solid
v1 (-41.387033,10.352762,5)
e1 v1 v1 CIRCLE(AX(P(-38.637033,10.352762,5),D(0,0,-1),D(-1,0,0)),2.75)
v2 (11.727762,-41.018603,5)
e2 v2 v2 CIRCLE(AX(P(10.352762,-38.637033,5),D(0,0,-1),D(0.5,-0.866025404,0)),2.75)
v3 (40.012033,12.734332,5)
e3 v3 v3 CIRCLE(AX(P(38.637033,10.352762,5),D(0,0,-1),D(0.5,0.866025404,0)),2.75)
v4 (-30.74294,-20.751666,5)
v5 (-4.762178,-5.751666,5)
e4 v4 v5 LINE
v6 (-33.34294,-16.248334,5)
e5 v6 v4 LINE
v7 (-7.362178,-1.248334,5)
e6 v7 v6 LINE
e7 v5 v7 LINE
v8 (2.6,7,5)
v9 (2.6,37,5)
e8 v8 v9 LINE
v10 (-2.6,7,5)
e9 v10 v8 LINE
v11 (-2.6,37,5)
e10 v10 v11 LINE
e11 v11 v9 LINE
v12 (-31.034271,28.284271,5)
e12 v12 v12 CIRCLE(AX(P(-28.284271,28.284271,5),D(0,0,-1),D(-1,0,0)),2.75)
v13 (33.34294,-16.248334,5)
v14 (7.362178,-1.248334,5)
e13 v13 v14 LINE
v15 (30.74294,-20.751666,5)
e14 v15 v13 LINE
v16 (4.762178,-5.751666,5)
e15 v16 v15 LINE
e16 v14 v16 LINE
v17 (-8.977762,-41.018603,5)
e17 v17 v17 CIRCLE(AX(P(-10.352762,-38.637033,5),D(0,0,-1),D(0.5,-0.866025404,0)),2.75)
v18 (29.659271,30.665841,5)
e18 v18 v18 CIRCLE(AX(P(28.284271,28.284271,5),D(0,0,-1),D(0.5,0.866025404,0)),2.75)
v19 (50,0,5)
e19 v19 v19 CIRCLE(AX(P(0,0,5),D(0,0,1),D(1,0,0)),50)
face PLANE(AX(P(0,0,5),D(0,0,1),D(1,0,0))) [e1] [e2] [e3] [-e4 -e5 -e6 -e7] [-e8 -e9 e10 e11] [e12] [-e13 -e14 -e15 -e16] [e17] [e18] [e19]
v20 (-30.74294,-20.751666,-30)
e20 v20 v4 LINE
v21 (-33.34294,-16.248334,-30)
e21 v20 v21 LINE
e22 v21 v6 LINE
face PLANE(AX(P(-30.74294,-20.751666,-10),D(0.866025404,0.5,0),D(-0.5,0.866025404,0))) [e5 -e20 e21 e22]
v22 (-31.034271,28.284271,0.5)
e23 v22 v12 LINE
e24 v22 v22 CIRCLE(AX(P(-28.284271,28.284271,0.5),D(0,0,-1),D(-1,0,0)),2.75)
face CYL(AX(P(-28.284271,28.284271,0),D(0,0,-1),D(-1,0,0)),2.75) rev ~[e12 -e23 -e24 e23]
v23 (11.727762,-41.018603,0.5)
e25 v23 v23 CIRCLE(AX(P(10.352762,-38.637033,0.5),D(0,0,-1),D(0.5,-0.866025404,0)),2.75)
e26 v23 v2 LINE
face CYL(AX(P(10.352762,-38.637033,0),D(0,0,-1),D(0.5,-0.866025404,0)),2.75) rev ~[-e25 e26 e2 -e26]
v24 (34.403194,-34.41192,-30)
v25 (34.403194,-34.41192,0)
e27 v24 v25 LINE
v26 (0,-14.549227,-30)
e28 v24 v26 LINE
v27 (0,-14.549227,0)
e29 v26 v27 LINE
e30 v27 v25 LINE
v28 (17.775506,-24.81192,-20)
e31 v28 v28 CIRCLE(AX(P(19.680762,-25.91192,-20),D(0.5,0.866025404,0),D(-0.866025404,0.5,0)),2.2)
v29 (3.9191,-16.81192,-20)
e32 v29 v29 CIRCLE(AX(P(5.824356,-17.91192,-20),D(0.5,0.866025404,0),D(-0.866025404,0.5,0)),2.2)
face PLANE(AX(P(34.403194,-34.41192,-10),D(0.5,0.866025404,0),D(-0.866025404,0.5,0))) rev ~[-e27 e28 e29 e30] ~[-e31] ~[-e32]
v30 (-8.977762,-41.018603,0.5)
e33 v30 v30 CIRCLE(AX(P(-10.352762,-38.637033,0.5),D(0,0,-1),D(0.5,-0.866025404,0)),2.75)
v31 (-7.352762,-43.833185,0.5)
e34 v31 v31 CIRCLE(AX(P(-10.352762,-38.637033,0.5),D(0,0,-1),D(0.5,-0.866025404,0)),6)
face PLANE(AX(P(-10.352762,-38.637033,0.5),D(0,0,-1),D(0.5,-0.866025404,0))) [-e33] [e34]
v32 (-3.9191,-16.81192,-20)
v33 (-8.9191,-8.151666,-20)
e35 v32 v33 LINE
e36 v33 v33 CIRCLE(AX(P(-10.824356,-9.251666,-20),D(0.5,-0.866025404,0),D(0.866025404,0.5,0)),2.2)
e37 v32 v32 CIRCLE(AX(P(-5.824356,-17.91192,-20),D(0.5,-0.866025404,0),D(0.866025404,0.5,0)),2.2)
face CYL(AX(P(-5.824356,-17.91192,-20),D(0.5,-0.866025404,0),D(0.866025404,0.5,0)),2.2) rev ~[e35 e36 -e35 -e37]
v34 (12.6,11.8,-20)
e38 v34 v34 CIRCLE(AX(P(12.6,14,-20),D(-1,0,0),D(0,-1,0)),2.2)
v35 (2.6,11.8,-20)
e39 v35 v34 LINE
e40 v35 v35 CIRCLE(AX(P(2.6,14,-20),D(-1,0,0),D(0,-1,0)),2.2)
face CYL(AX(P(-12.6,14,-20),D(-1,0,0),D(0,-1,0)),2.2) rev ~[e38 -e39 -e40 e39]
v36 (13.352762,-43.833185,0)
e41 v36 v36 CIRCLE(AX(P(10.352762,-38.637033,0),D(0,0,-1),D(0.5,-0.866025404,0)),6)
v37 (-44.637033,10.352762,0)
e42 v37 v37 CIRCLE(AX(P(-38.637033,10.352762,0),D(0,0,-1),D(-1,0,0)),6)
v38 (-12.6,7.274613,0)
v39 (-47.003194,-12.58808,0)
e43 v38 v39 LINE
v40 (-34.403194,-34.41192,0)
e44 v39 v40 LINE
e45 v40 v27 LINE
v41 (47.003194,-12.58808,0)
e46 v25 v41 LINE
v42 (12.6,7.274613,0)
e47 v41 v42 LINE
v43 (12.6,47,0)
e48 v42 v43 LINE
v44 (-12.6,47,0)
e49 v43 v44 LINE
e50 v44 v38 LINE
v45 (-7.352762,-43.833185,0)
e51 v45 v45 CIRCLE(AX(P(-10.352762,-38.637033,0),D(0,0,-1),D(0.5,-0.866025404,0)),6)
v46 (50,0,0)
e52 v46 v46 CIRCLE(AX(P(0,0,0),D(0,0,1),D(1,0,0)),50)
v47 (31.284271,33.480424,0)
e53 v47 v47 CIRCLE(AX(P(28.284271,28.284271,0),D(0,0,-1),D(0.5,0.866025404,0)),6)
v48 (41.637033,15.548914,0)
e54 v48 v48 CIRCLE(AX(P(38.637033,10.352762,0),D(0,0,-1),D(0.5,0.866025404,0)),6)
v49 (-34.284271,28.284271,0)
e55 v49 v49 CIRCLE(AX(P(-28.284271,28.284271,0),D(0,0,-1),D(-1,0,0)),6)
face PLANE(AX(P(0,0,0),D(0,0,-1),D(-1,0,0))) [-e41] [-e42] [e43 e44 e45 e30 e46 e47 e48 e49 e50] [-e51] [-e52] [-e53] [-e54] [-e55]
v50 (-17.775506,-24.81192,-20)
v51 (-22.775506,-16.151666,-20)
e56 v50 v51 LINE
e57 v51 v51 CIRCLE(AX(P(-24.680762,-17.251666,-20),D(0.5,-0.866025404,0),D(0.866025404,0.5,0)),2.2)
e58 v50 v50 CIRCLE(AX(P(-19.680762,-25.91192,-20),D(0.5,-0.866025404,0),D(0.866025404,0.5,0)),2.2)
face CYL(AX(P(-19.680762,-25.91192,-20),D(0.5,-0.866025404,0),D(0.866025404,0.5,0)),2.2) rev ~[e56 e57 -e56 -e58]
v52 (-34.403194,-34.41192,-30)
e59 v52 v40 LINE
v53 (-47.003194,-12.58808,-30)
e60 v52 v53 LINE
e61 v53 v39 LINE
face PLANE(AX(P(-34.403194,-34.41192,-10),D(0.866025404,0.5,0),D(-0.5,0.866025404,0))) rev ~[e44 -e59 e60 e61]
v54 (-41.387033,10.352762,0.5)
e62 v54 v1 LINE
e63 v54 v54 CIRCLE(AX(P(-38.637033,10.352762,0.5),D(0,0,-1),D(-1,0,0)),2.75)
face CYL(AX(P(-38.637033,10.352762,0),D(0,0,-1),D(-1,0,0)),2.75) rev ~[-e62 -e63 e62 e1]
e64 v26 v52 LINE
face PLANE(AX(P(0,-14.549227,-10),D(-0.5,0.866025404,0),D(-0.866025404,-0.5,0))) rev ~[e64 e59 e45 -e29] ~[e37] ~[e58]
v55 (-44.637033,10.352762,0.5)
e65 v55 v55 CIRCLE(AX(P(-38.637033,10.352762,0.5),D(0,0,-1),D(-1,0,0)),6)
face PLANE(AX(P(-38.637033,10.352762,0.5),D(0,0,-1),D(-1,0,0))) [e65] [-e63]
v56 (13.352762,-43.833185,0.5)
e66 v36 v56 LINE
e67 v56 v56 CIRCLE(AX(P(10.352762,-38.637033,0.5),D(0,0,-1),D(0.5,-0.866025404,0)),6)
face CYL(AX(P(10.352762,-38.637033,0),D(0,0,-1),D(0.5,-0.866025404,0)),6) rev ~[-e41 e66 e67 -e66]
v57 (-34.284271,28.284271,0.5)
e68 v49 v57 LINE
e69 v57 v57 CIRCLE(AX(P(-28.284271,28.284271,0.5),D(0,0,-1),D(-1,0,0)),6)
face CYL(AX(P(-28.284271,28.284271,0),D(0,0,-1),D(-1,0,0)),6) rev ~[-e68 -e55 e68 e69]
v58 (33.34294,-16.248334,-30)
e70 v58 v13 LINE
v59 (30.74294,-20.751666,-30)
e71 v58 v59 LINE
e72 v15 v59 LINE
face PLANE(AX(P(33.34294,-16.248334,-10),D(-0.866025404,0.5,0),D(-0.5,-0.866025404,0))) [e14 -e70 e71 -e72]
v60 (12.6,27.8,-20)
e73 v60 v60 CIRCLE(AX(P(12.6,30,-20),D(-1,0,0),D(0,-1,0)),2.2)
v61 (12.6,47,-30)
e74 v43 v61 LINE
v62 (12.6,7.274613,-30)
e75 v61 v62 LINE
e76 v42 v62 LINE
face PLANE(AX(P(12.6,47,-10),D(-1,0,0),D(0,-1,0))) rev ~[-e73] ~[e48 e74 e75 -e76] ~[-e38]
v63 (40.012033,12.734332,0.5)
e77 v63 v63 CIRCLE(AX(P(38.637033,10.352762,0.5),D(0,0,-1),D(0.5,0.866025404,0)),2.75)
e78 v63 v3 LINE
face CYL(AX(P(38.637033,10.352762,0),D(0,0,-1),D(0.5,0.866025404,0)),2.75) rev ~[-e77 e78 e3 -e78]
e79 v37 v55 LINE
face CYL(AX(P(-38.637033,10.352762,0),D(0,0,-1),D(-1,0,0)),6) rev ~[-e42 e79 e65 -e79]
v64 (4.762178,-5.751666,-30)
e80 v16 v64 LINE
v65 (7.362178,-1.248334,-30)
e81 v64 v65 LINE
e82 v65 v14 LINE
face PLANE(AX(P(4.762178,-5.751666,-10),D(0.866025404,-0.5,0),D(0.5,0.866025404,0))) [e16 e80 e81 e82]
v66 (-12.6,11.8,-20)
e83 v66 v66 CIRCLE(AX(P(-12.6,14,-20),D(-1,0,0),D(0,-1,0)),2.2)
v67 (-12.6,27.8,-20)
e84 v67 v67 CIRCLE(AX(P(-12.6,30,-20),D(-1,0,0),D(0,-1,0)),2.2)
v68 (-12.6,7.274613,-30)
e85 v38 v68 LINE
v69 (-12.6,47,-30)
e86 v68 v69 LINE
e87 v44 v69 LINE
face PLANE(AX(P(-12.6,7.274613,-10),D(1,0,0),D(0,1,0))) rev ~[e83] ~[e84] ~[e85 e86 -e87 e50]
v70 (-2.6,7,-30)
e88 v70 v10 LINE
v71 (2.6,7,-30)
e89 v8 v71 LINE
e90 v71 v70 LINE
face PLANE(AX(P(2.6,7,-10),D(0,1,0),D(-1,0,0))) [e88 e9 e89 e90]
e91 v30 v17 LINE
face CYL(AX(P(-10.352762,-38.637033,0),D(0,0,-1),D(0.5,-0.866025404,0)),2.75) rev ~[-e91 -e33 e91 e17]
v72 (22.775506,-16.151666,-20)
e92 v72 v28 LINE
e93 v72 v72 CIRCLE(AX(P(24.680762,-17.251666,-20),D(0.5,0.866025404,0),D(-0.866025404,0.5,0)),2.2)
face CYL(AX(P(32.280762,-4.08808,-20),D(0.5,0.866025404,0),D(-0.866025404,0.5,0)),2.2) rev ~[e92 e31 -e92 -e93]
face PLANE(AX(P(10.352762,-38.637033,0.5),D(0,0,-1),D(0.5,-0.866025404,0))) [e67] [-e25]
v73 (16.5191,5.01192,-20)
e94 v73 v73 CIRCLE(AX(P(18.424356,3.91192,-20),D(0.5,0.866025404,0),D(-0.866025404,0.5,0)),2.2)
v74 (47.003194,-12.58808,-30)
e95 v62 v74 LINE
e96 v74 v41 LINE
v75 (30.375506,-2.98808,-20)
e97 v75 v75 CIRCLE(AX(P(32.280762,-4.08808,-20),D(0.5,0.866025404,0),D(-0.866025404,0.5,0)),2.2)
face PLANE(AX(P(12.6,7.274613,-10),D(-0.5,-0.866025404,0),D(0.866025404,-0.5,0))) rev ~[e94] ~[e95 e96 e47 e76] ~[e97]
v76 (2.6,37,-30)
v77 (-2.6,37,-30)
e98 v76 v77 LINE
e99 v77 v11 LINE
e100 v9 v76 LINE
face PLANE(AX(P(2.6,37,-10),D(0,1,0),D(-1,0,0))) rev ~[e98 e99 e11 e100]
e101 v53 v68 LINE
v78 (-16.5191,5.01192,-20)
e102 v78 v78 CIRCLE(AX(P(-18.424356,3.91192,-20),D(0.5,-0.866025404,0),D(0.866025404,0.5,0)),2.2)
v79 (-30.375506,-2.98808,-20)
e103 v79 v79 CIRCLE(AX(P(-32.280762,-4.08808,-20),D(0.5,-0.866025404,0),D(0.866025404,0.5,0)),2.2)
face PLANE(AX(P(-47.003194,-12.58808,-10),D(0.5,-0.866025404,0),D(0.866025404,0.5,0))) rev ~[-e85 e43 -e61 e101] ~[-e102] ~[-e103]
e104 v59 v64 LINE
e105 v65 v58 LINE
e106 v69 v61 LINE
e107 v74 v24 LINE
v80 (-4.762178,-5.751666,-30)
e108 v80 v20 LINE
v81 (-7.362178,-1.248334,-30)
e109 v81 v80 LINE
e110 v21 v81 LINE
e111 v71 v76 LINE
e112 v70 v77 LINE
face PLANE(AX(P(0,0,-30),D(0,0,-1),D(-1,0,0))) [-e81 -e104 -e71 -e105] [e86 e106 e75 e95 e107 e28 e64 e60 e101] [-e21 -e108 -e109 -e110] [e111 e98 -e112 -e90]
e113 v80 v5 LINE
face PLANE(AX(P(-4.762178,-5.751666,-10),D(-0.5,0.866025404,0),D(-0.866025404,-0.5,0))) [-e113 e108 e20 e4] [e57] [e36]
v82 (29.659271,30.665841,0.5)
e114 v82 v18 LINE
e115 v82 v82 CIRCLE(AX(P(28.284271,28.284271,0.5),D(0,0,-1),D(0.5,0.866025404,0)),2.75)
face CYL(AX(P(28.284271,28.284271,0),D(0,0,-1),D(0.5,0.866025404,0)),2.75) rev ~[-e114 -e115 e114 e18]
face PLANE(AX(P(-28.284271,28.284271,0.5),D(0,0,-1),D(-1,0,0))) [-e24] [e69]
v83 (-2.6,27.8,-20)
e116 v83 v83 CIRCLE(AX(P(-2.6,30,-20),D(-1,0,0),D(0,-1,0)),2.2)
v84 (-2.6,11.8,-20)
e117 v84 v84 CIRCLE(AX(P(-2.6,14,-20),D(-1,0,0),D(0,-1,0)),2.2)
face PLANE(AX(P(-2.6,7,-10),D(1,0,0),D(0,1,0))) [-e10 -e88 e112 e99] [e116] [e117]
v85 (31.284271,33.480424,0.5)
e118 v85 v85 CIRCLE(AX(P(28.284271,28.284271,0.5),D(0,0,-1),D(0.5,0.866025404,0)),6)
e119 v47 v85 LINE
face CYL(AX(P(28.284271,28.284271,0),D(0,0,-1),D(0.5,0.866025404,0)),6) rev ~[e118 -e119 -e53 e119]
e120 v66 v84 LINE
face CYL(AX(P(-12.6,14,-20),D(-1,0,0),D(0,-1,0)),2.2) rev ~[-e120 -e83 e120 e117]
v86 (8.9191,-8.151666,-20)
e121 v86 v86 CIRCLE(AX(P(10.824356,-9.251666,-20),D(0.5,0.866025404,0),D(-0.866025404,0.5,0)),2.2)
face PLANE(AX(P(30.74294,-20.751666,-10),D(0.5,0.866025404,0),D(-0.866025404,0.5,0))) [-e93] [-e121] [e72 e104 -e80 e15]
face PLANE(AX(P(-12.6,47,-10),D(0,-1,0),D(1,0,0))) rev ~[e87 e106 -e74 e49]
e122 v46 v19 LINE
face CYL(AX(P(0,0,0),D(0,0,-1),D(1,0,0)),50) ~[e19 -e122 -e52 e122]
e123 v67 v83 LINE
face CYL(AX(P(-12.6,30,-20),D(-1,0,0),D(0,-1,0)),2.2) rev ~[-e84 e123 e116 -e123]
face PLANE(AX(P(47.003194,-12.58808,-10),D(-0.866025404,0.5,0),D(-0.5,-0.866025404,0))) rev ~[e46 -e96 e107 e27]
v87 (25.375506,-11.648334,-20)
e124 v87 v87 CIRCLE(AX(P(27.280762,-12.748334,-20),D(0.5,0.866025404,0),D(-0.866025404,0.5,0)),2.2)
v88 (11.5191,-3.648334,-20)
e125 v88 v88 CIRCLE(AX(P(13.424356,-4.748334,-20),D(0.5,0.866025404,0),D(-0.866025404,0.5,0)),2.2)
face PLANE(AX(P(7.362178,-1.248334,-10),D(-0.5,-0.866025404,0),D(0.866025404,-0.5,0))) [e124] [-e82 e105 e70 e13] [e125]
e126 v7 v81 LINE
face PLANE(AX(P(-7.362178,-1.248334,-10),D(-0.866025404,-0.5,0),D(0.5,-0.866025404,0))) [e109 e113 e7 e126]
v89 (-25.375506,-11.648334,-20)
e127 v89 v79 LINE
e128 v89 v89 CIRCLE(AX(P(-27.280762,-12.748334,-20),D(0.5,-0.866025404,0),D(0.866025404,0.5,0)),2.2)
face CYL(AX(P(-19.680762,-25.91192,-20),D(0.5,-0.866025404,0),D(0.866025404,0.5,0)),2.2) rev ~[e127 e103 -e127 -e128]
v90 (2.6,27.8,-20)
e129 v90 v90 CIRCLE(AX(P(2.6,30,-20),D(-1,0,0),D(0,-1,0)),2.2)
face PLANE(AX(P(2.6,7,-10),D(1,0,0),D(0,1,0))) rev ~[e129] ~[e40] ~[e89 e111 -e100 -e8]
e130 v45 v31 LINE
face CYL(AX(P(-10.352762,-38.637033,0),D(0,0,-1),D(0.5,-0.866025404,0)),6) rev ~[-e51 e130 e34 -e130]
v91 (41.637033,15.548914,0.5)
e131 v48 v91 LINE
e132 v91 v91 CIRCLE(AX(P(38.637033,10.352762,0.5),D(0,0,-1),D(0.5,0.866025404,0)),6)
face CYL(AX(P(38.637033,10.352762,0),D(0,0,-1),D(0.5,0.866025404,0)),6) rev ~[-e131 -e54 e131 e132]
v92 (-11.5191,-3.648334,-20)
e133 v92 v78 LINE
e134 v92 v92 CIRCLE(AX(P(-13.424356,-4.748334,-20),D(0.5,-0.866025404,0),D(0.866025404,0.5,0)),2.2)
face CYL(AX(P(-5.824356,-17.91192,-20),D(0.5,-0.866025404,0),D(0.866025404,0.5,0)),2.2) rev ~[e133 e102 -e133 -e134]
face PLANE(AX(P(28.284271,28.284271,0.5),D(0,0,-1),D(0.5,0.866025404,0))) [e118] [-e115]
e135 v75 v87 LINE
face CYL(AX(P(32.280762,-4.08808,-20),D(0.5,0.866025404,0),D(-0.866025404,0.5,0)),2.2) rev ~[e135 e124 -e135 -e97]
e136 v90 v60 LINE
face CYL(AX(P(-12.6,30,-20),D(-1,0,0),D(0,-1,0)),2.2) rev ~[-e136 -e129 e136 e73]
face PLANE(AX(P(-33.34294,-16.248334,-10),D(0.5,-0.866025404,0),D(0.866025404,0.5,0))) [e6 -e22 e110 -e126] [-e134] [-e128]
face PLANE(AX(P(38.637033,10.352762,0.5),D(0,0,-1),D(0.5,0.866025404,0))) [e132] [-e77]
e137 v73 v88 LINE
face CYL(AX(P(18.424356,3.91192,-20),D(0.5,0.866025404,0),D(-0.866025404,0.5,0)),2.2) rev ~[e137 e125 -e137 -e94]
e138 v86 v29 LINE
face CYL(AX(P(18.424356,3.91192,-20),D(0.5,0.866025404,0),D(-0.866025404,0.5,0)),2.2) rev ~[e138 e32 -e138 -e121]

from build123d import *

# Parameters (mm, degrees)
SKETCH_1_R               = 50
SKETCH_1_W               = 5.2
SKETCH_1_H               = 30
EXTRUDE_1_DEPTH          = 5
SKETCH_2_R               = 60
SKETCH_2_W               = 5.2
SKETCH_2_H               = 30
EXTRUDE_2_DEPTH          = 10
CUT_EXTRUDE_START        = -10
SKETCH_4_R               = 60
CUT_EXTRUDE_1_DEPTH      = 10
SKETCH_8_W               = 5.2
SKETCH_8_H               = 30
EXTRUDE_5_DEPTH          = 20
SKETCH_6_R               = 2.2
CUT_EXTRUDE_2_DEPTH      = 42
PATTERN_CIRCULAR_1_COUNT = 3
SKETCH_9_R               = 2.75
CUT_EXTRUDE_3_DEPTH      = 10
SKETCH_10_R              = 6
CUT_EXTRUDE_4_DEPTH      = 0.5
PATTERN_CIRCULAR_2_COUNT = 3


with BuildPart() as part:
    # 草图1 → 凸台-拉伸1 (new body)
    with BuildSketch(Plane.XY):
        Circle(SKETCH_1_R)
        with Locations((0, 22)):
            Rectangle(SKETCH_1_W, SKETCH_1_H, mode=Mode.SUBTRACT)
        Polygon((4.762177826, -5.75166605), (30.74293994, -20.75166605), (33.34293994, -16.24833395), (7.362177826, -1.24833395), align=None, mode=Mode.SUBTRACT)
        Polygon((-7.362177826, -1.24833395), (-33.34293994, -16.24833395), (-30.74293994, -20.75166605), (-4.762177826, -5.75166605), align=None, mode=Mode.SUBTRACT)
    extrude(amount=EXTRUDE_1_DEPTH)

    # 草图2 → 凸台-拉伸2 (add)
    with BuildSketch(Plane.XY):
        Circle(SKETCH_2_R)
        with Locations((0, 22)):
            Rectangle(SKETCH_2_W, SKETCH_2_H, mode=Mode.SUBTRACT)
        Polygon((7.362177826, -1.24833395), (4.762177826, -5.75166605), (30.74293994, -20.75166605), (33.34293994, -16.24833395), align=None, mode=Mode.SUBTRACT)
        Polygon((-4.762177826, -5.75166605), (-7.362177826, -1.24833395), (-33.34293994, -16.24833395), (-30.74293994, -20.75166605), align=None, mode=Mode.SUBTRACT)
    extrude(amount=-EXTRUDE_2_DEPTH)

    # 草图4 → 切除-拉伸1 (cut)
    with BuildSketch(Plane(origin=(0, 0, -10), x_dir=(-1, 0, 0), z_dir=(0, 0, -1)).offset(CUT_EXTRUDE_START)):
        Circle(SKETCH_4_R)
        Polygon((-47.003193978, -12.588079912), (-12.6, 7.274613392), (-12.6, 47), (12.6, 47), (12.6, 7.274613392), (47.003193978, -12.588079912), (34.403193978, -34.411920088), (0, -14.549226784), (-34.403193978, -34.411920088), align=None, mode=Mode.SUBTRACT)
    extrude(amount=CUT_EXTRUDE_1_DEPTH, mode=Mode.SUBTRACT)

    # 草图8 → 凸台-拉伸5 (add)
    with BuildSketch(Plane(origin=(0, 0, -10), x_dir=(-1, 0, 0), z_dir=(0, 0, -1))):
        Polygon((47.003193978, -12.588079912), (12.6, 7.274613392), (12.6, 47), (-12.6, 47), (-12.6, 7.274613392), (-47.003193978, -12.588079912), (-34.403193978, -34.411920088), (0, -14.549226784), (34.403193978, -34.411920088), align=None)
        with Locations((0, 22)):
            Rectangle(SKETCH_8_W, SKETCH_8_H, mode=Mode.SUBTRACT)
        Polygon((-4.762177826, -5.75166605), (-7.362177826, -1.24833395), (-33.34293994, -16.24833395), (-30.74293994, -20.75166605), align=None, mode=Mode.SUBTRACT)
        Polygon((7.362177826, -1.24833395), (4.762177826, -5.75166605), (30.74293994, -20.75166605), (33.34293994, -16.24833395), align=None, mode=Mode.SUBTRACT)
    extrude(amount=EXTRUDE_5_DEPTH)

    # 草图6 → 切除-拉伸2 (cut)
    with BuildSketch(Plane(origin=(6.3, -10.911920088, 0), x_dir=(0.8660254037844384, 0.5000000000000004, 0), z_dir=(0.5000000000000004, -0.8660254037844384, 0))):
        with Locations((-30, -20)):
            Circle(SKETCH_6_R)
        with Locations((-14, -20)):
            Circle(SKETCH_6_R)
    cut_extrude_2 = extrude(amount=-CUT_EXTRUDE_2_DEPTH, mode=Mode.SUBTRACT)

    # 阵列(圆周)1: 切除-拉伸2 ×3 about axis
    pattern_circular_1_axis = Axis((0, 0, 5), (0, 0, -1))
    for i in range(1, PATTERN_CIRCULAR_1_COUNT):
        add(cut_extrude_2.rotate(pattern_circular_1_axis, i * 360 / PATTERN_CIRCULAR_1_COUNT), mode=Mode.SUBTRACT)

    # 草图9 → 切除-拉伸3 (cut)
    with BuildSketch(Plane(origin=(0, 0, 0), x_dir=(-1, 0, 0), z_dir=(0, 0, -1))):
        with Locations((28.284271247, 28.284271247)):
            Circle(SKETCH_9_R)
        with Locations((38.637033052, 10.352761804)):
            Circle(SKETCH_9_R)
    cut_extrude_3 = extrude(amount=-CUT_EXTRUDE_3_DEPTH, mode=Mode.SUBTRACT)

    # 草图10 → 切除-拉伸4 (cut)
    with BuildSketch(Plane(origin=(0, 0, 0), x_dir=(-1, 0, 0), z_dir=(0, 0, -1))):
        with Locations((28.284271247, 28.284271247)):
            Circle(SKETCH_10_R)
        with Locations((38.637033052, 10.352761804)):
            Circle(SKETCH_10_R)
    cut_extrude_4 = extrude(amount=-CUT_EXTRUDE_4_DEPTH, mode=Mode.SUBTRACT)

    # 阵列(圆周)2: 切除-拉伸3, 切除-拉伸4 ×3 about axis
    pattern_circular_2_axis = Axis((0, 0, 0), (0, 0, 1))
    add([cut_extrude_3.rotate(pattern_circular_2_axis, i * 360 / PATTERN_CIRCULAR_2_COUNT) for i in range(1, PATTERN_CIRCULAR_2_COUNT)], mode=Mode.SUBTRACT)
    add([cut_extrude_4.rotate(pattern_circular_2_axis, i * 360 / PATTERN_CIRCULAR_2_COUNT) for i in range(1, PATTERN_CIRCULAR_2_COUNT)], mode=Mode.SUBTRACT)


solid = part.part
